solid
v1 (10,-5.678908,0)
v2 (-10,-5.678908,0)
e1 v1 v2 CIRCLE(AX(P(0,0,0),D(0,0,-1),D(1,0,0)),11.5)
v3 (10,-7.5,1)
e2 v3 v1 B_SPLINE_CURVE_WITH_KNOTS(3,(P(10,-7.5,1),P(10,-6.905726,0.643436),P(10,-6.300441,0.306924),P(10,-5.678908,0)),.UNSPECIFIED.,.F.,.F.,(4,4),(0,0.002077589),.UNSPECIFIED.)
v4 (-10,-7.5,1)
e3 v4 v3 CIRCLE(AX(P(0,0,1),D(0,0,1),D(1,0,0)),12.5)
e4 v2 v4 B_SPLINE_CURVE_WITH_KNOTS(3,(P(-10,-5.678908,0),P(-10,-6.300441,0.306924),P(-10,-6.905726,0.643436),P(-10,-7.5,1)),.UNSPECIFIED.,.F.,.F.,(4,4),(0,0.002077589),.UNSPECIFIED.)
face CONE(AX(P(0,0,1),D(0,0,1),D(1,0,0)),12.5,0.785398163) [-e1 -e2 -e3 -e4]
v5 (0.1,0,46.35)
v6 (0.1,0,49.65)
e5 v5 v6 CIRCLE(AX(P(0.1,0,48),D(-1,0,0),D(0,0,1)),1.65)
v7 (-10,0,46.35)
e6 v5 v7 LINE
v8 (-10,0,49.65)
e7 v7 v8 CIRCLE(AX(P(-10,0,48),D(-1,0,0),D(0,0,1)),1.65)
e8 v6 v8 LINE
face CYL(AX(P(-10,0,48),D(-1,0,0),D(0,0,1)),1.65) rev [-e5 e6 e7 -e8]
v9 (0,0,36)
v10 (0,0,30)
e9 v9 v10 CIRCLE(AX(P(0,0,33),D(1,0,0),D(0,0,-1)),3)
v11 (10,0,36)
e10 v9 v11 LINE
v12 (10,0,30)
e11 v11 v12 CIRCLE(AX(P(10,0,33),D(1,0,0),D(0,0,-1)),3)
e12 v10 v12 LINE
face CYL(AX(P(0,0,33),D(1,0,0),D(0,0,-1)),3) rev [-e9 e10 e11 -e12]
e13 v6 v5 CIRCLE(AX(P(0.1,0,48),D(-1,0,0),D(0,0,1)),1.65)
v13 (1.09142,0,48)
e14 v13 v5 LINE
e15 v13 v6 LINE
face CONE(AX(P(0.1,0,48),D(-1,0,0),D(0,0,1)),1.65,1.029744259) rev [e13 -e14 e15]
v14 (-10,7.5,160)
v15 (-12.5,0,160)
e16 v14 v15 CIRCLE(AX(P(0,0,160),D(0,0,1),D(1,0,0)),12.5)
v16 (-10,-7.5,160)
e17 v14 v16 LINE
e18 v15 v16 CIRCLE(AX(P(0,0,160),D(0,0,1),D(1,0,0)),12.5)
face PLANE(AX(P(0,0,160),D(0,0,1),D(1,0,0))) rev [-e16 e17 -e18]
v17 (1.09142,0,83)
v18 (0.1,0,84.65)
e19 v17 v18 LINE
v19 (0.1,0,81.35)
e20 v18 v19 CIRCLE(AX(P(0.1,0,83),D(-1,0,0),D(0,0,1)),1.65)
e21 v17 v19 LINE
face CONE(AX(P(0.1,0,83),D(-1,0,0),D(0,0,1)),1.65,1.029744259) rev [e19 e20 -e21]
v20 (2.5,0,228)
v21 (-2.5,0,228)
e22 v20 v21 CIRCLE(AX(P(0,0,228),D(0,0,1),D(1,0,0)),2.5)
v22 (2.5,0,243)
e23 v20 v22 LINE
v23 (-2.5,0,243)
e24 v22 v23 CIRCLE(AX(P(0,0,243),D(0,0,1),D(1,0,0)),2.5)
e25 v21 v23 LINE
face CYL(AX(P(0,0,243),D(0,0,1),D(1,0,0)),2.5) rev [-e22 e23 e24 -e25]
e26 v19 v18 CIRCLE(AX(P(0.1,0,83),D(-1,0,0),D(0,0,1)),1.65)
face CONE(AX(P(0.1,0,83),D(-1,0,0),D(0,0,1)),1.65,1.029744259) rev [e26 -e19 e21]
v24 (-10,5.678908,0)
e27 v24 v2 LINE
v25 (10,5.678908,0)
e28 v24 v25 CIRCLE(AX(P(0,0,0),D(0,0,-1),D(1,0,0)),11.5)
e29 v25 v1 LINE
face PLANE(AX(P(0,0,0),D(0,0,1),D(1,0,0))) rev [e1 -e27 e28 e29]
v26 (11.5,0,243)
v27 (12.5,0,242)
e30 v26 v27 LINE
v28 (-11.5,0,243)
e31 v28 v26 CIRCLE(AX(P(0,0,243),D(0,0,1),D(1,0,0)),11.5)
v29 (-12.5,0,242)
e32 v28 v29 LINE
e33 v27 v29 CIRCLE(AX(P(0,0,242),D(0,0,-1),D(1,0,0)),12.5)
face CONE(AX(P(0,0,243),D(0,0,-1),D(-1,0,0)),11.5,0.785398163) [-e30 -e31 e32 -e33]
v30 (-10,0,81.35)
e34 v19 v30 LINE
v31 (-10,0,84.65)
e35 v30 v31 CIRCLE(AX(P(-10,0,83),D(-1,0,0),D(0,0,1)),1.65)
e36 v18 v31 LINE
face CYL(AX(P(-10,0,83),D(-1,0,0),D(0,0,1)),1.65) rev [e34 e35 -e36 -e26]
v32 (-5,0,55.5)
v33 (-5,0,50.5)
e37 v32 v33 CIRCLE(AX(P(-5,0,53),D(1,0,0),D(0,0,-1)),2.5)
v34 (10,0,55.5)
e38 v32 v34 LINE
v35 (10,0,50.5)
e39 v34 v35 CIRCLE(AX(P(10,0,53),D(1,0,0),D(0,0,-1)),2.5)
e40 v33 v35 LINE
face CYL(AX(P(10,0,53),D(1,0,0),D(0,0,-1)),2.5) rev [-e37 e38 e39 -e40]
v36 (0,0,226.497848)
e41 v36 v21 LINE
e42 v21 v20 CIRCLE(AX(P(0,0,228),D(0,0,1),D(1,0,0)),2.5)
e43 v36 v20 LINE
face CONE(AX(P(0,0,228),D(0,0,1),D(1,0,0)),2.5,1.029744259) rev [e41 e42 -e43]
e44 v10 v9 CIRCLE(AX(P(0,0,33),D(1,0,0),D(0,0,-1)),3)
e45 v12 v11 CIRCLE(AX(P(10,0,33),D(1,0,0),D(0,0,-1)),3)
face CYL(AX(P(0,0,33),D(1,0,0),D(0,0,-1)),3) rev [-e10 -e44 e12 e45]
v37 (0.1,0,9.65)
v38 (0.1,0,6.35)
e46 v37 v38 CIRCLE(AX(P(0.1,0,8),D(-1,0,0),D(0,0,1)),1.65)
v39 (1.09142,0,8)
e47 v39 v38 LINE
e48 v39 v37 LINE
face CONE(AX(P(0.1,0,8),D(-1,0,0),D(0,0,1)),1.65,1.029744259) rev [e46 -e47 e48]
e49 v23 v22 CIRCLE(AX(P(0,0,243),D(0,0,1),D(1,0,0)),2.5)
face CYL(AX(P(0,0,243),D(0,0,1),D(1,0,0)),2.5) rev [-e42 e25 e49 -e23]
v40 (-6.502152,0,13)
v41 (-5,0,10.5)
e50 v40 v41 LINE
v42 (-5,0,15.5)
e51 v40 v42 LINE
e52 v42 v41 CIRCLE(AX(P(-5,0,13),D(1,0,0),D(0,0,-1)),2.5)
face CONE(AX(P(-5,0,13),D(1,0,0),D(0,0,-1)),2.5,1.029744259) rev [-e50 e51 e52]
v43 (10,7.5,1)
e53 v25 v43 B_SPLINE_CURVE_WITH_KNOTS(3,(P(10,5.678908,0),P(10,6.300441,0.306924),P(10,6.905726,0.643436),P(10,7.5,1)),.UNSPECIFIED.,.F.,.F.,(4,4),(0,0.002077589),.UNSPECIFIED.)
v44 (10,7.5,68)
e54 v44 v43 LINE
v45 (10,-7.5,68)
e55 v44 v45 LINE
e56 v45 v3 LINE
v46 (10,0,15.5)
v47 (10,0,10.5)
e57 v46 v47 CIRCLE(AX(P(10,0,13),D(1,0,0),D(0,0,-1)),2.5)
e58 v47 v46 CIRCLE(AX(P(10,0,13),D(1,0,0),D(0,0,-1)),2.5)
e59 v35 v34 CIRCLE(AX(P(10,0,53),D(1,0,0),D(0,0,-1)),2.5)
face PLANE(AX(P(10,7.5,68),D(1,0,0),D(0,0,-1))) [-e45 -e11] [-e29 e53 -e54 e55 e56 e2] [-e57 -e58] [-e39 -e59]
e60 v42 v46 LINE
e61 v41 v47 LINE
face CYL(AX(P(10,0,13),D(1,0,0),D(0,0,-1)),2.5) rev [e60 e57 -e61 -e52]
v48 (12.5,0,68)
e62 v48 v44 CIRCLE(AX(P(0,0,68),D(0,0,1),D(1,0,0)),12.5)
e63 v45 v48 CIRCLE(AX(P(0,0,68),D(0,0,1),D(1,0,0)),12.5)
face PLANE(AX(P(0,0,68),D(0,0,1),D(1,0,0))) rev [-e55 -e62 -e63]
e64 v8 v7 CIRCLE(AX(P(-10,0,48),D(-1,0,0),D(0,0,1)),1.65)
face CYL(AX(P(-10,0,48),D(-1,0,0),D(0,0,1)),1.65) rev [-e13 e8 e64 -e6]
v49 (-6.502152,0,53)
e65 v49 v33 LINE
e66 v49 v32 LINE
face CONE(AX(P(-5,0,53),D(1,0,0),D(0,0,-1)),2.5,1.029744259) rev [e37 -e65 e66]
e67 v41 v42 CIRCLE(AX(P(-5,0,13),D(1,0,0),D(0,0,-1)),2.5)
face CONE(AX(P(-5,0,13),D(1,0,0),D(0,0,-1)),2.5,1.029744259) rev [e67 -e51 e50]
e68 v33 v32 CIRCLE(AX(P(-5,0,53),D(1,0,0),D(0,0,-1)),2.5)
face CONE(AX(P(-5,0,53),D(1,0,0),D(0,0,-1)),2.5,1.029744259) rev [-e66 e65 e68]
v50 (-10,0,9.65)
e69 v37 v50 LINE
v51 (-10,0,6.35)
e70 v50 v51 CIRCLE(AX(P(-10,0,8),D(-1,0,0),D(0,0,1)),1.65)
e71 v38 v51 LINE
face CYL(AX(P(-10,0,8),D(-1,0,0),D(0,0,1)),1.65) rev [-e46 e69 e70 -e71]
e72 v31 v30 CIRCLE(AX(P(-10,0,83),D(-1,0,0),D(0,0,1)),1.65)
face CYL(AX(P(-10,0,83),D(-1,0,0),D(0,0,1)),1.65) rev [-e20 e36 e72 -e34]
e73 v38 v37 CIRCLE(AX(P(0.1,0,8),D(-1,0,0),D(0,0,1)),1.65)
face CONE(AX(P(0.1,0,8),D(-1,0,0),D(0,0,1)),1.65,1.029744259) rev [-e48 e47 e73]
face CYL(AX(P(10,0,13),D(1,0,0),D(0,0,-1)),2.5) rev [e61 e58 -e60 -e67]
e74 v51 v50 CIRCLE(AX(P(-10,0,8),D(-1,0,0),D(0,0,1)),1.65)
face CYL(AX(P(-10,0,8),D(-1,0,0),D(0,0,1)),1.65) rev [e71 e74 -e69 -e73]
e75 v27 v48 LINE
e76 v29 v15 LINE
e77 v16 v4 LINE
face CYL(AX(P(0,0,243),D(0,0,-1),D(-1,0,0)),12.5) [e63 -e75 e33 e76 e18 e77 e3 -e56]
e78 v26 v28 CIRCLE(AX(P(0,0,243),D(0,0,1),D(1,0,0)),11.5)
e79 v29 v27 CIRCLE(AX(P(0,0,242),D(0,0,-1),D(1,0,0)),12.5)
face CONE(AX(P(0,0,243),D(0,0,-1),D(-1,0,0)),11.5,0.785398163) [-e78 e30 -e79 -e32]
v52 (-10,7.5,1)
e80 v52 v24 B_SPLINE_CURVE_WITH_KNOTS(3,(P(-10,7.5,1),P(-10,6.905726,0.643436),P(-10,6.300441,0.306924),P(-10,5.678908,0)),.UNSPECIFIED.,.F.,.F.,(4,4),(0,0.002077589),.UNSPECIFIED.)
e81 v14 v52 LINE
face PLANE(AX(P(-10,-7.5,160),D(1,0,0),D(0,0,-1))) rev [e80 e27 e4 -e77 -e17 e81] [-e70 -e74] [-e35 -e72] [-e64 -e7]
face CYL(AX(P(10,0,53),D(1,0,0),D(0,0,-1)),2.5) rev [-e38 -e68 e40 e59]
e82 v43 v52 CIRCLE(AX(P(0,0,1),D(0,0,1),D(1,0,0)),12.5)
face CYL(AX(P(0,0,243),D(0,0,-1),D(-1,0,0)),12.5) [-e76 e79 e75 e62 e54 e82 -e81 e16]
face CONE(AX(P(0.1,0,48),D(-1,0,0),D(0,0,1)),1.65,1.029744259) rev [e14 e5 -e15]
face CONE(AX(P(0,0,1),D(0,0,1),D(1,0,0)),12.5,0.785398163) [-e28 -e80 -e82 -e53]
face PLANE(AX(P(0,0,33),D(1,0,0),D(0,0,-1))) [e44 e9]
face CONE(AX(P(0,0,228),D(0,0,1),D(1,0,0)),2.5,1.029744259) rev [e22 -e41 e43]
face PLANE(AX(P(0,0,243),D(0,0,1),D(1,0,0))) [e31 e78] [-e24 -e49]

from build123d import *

# Parameters (mm, degrees)
SKETCH1_R             = 12.5
BOSS_EXTRUDE1_DEPTH   = 243
SKETCH2_W             = 20
SKETCH2_H             = 15
CUT_EXTRUDE1_DEPTH    = 68
M6_TAPPED_HOLE1_D     = 5
M6_TAPPED_HOLE1_DEPTH = 15
M6_TAPPED_HOLE1_TIP   = 1.502151548
M6_TAPPED_HOLE2_D     = 5
M6_TAPPED_HOLE2_DEPTH = 15
M6_TAPPED_HOLE2_TIP   = 1.502151548
SKETCH7_W             = 2.5
SKETCH7_H             = 15
CUT_EXTRUDE2_DEPTH    = 160
M4_TAPPED_HOLE1_D     = 3.3
M4_TAPPED_HOLE1_DEPTH = 10.1
M4_TAPPED_HOLE1_TIP   = 0.991420021
SKETCH10_R            = 3
CUT_EXTRUDE3_DEPTH    = 10
CHAMFER1_SIZE         = 1


with BuildPart() as part:
    # Sketch1 → Boss-Extrude1 (new body)
    with BuildSketch(Plane.XY):
        Circle(SKETCH1_R)
    extrude(amount=BOSS_EXTRUDE1_DEPTH)

    # Sketch2 → Cut-Extrude1 (cut)
    with BuildSketch(Plane.XY):
        with Locations((20, 0)):
            Rectangle(SKETCH2_W, SKETCH2_H)
    extrude(amount=CUT_EXTRUDE1_DEPTH, mode=Mode.SUBTRACT)

    # M6 Tapped Hole1
    with Locations(Plane.XY.offset(243)):
        with Locations((0, 0)):
            Hole(M6_TAPPED_HOLE1_D / 2, depth=M6_TAPPED_HOLE1_DEPTH)
            with Locations((0, 0, -(M6_TAPPED_HOLE1_DEPTH + M6_TAPPED_HOLE1_TIP / 2))):  # 118° drill point
                Cone(0, M6_TAPPED_HOLE1_D / 2, M6_TAPPED_HOLE1_TIP, mode=Mode.SUBTRACT)

    # M6 Tapped Hole2
    with Locations(Plane(origin=(10, 0, 0), x_dir=(0, 0, -1), z_dir=(1, 0, 0))):
        with Locations((-13, 0), (-53, 0)):
            Hole(M6_TAPPED_HOLE2_D / 2, depth=M6_TAPPED_HOLE2_DEPTH)
            with Locations((0, 0, -(M6_TAPPED_HOLE2_DEPTH + M6_TAPPED_HOLE2_TIP / 2))):  # 118° drill point
                Cone(0, M6_TAPPED_HOLE2_D / 2, M6_TAPPED_HOLE2_TIP, mode=Mode.SUBTRACT)

    # Sketch7 → Cut-Extrude2 (cut)
    with BuildSketch(Plane(origin=(0, 0, 0), x_dir=(-1, 0, 0), z_dir=(0, 0, -1))):
        with Locations((11.25, 0)):
            Rectangle(SKETCH7_W, SKETCH7_H)
    extrude(amount=-CUT_EXTRUDE2_DEPTH, mode=Mode.SUBTRACT)

    # M4 Tapped Hole1
    with Locations(Plane.ZY.offset(10)):
        with Locations((8, 0), (83, 0), (48, 0)):
            Hole(M4_TAPPED_HOLE1_D / 2, depth=M4_TAPPED_HOLE1_DEPTH)
            with Locations((0, 0, -(M4_TAPPED_HOLE1_DEPTH + M4_TAPPED_HOLE1_TIP / 2))):  # 118° drill point
                Cone(0, M4_TAPPED_HOLE1_D / 2, M4_TAPPED_HOLE1_TIP, mode=Mode.SUBTRACT)

    # Sketch10 → Cut-Extrude3 (cut)
    with BuildSketch(Plane(origin=(10, 0, 0), x_dir=(0, 0, -1), z_dir=(1, 0, 0))):
        with Locations((-33, 0)):
            Circle(SKETCH10_R)
    extrude(amount=-CUT_EXTRUDE3_DEPTH, mode=Mode.SUBTRACT)

    # Chamfer1
    chamfer1_edges = [part.edges().sort_by_distance(p)[0] for p in [
        (0, 12.5, 0),
        (0, -12.5, 0),
        (-12.5, 0, 243),
    ]]
    chamfer(chamfer1_edges, length=CHAMFER1_SIZE)


solid = part.part
